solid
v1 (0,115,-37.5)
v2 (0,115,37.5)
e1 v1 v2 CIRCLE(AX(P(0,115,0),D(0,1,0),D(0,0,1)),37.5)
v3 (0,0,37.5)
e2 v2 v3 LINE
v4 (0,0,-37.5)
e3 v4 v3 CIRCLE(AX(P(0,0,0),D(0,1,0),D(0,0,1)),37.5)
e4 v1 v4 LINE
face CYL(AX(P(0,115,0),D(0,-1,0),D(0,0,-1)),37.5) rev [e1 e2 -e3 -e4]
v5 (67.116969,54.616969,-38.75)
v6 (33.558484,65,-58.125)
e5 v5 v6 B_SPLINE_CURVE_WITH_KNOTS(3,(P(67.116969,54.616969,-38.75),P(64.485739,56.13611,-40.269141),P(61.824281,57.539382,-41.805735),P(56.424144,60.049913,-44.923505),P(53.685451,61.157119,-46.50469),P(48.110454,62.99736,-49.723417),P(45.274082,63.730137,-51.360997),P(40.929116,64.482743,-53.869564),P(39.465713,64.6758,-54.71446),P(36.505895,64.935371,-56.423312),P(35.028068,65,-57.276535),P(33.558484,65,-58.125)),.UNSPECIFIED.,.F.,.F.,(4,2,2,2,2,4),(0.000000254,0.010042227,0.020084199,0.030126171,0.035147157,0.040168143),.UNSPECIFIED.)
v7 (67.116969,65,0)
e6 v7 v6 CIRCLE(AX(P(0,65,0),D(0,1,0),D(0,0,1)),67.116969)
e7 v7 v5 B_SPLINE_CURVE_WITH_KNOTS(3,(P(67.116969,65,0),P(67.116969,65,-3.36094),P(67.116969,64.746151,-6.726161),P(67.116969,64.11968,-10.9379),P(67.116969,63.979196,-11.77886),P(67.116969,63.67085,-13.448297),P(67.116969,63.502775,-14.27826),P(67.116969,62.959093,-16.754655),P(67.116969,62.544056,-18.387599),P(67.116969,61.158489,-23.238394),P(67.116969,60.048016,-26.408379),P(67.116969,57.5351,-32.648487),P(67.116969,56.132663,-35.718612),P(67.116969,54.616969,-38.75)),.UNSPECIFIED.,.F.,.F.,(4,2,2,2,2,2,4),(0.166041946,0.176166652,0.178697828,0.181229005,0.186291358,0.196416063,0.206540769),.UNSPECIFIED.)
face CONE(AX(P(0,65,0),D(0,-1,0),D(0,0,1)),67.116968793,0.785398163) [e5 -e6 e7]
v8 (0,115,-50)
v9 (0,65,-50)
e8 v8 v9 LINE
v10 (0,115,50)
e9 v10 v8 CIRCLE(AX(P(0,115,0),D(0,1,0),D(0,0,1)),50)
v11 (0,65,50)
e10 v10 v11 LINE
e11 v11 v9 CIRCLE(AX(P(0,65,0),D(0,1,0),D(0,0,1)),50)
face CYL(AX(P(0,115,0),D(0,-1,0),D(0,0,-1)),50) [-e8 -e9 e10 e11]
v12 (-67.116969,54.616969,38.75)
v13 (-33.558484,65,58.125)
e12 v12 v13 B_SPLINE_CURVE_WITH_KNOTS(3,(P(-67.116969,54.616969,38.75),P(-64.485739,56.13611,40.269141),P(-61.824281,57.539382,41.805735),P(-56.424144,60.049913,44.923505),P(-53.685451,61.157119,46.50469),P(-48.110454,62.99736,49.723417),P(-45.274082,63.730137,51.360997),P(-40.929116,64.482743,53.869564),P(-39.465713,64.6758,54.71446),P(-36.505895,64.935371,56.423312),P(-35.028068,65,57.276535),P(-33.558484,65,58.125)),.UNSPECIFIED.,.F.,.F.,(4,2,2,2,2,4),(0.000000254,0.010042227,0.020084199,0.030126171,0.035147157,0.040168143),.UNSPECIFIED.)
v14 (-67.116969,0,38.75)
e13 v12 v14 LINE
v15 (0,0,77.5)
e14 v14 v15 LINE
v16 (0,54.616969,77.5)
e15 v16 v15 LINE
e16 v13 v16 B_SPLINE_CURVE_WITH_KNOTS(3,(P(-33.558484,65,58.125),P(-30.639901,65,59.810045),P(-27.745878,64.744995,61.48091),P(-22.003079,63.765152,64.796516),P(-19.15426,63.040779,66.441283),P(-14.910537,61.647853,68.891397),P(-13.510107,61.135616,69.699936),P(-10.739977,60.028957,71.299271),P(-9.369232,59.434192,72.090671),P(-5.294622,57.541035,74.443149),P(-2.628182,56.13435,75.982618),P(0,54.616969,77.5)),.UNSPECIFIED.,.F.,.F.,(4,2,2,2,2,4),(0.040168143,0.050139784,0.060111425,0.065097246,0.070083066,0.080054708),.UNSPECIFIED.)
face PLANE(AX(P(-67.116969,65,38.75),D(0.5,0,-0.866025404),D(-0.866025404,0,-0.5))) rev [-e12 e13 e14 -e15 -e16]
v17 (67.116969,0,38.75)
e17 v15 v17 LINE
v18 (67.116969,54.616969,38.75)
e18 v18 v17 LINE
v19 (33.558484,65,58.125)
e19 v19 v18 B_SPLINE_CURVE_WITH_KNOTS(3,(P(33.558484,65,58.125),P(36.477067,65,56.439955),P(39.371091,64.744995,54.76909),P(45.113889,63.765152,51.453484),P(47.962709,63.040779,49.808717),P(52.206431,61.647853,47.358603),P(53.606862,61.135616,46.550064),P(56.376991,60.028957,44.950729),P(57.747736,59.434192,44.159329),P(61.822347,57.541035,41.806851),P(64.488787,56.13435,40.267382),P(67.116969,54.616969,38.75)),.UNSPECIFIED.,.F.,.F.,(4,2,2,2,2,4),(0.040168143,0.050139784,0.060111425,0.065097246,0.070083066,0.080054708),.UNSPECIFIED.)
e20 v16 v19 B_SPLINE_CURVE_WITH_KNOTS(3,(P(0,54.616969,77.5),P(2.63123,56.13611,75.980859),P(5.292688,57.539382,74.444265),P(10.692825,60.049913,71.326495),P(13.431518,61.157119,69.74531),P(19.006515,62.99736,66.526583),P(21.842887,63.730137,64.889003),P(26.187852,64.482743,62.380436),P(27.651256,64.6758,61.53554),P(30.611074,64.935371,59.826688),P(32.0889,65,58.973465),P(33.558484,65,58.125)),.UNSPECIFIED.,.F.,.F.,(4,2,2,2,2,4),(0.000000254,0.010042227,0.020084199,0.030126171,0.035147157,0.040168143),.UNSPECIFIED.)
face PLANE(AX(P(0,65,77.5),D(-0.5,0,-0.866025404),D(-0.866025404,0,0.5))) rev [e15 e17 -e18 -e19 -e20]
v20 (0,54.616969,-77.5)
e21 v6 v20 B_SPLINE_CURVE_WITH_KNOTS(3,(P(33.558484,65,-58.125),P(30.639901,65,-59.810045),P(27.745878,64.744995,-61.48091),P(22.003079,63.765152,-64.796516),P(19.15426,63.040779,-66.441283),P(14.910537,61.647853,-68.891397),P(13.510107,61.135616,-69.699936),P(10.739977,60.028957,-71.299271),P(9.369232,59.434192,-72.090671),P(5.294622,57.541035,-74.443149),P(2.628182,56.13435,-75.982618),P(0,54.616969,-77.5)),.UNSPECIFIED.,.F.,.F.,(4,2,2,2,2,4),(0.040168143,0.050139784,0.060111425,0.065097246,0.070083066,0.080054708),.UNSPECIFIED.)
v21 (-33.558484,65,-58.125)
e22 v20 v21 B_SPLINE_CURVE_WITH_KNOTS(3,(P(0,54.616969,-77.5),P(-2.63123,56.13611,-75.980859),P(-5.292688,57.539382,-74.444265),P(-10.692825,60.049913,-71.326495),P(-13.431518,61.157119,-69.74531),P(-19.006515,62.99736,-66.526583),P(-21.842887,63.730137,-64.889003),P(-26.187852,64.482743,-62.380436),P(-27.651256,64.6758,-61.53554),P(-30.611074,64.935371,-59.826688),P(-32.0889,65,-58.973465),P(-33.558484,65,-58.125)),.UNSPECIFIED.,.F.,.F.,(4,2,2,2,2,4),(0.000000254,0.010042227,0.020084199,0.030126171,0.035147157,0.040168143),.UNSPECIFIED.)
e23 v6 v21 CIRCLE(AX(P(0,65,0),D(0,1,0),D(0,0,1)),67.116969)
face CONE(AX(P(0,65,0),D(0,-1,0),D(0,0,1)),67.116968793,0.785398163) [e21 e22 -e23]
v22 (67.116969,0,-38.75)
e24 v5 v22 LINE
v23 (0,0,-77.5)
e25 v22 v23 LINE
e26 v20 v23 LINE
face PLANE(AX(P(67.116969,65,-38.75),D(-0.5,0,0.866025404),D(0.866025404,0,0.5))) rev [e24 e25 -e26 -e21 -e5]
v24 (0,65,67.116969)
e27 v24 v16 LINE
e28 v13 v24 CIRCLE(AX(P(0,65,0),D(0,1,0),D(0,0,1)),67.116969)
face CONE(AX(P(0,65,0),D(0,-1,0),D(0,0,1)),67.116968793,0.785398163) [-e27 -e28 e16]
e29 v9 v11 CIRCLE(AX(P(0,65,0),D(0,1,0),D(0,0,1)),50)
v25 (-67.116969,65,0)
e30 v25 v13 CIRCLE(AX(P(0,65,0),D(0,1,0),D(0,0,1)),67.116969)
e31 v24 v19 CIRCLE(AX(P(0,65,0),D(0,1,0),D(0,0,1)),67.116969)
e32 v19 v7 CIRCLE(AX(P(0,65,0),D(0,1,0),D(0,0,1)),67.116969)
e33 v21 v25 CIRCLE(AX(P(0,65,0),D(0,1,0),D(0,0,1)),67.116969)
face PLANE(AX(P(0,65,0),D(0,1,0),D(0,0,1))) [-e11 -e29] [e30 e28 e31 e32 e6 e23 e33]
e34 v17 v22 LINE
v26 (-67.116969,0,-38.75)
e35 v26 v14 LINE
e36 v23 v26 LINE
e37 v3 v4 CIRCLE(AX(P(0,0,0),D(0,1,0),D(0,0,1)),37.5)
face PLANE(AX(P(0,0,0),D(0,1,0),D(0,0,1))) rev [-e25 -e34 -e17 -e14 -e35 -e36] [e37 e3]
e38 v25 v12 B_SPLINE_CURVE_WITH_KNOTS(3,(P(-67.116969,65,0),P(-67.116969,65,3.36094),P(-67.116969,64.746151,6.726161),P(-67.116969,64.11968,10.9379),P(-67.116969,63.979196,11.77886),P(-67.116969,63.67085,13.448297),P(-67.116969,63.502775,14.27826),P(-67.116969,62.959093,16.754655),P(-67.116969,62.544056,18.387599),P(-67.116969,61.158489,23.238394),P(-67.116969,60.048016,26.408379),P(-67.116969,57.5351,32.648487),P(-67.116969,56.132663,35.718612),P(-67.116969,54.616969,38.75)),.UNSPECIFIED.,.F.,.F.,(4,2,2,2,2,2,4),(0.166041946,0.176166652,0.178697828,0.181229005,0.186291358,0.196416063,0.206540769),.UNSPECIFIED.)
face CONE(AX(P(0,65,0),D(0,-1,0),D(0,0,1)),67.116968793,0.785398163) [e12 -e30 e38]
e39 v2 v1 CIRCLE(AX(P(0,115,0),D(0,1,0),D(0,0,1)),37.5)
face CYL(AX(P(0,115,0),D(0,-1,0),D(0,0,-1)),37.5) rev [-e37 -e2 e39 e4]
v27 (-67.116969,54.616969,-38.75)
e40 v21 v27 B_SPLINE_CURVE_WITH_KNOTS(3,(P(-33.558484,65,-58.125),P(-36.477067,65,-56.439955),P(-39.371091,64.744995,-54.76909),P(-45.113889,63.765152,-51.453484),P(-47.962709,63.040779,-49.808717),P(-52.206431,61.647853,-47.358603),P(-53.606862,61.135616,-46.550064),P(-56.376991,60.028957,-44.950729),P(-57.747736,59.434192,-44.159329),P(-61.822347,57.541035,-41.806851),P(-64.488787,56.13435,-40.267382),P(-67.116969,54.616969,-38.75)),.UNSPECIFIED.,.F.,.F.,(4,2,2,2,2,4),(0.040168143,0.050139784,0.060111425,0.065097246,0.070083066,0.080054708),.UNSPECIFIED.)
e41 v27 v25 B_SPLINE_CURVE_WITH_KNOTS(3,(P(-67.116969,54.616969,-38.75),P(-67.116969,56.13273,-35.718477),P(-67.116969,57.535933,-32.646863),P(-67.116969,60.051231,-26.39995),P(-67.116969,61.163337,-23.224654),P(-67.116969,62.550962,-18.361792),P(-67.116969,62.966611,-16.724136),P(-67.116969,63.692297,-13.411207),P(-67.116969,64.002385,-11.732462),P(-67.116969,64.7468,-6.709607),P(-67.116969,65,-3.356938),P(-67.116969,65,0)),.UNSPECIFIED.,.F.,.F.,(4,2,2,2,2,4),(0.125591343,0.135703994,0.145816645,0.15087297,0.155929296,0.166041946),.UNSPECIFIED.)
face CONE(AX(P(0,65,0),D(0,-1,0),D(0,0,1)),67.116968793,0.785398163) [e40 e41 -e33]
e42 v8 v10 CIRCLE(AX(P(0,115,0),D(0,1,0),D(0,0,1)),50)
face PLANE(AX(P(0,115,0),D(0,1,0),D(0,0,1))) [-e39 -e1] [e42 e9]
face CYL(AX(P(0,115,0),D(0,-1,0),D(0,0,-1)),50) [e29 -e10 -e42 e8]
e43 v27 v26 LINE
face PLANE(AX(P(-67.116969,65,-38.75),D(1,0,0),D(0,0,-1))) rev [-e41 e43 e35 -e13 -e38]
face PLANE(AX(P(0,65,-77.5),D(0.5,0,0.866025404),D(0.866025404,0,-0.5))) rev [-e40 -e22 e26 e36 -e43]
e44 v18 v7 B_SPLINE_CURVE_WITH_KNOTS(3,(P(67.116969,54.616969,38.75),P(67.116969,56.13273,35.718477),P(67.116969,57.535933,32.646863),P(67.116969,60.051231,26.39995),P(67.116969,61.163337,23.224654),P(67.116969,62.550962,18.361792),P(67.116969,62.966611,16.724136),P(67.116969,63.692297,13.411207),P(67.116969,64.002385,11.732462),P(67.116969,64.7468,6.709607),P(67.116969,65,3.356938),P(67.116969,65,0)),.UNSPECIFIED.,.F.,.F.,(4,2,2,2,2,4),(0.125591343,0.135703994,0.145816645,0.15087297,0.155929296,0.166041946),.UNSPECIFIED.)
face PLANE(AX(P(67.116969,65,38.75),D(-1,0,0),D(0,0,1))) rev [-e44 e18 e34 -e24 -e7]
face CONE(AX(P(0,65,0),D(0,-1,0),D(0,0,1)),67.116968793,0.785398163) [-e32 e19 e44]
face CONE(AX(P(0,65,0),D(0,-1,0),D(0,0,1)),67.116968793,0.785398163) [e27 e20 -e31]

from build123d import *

# Parameters (mm, degrees)
HEX_BODY_DEPTH                  = 65
CORNER_CHAMFER_SKETCH_OUTSIDE_W = 309.254
CORNER_CHAMFER_SKETCH_OUTSIDE_H = 330.02
CORNER_CHAMFER_SKETCH_OUTSIDE_R = 67.116968793
HEX_CORNER_CHAMFER_45DEG_DEPTH  = 65
HEX_CORNER_CHAMFER_45DEG_DRAFT  = -45
LOCKING_COLLAR_SKETCH_R         = 50
LOCKING_COLLAR_SKETCH_R_2       = 37.5
LOCKING_COLLAR_DEPTH            = 50
NUT_START                       = -120
SKETCH3_2_R                     = 37.5
NUT_BORE_DEPTH                  = 120


with BuildPart() as part:
    # Hex Profile Sketch → Hex Body (new body)
    with BuildSketch(Plane(origin=(0, 0, 0), x_dir=(1, 0, 0), z_dir=(0, 1, 0))):
        Polygon((0, -77.5), (67.116968793, -38.75), (67.116968793, 38.75), (0, 77.5), (-67.116968793, 38.75), (-67.116968793, -38.75), align=None)
    extrude(amount=HEX_BODY_DEPTH)


with BuildPart() as hex_corner_chamfer_45deg_tool:
    # Corner Chamfer Sketch outside → Hex Corner Chamfer 45deg (with draft: the straight prism first)
    with BuildSketch(Plane(origin=(0, 65, 0), x_dir=(1, 0, 0), z_dir=(0, 1, 0))):
        Rectangle(CORNER_CHAMFER_SKETCH_OUTSIDE_W, CORNER_CHAMFER_SKETCH_OUTSIDE_H)
        Circle(CORNER_CHAMFER_SKETCH_OUTSIDE_R, mode=Mode.SUBTRACT)
    extrude(amount=-HEX_CORNER_CHAMFER_45DEG_DEPTH)
    # Hex Corner Chamfer 45deg: the draft: its side faces are tilted about the plane it starts from
    hex_corner_chamfer_45deg_sides = [hex_corner_chamfer_45deg_tool.faces().sort_by_distance(p)[0] for p in [
        (0, 32.5, 165.01),
        (154.627, 32.5, 0),
        (0, 32.5, -165.01),
        (-154.627, 32.5, 0),
        (-67.116968793, 32.5, 0),
    ]]
    draft(hex_corner_chamfer_45deg_sides, Plane(origin=(0, 65, 0), x_dir=(1, 0, 0), z_dir=(0, 1, 0)), HEX_CORNER_CHAMFER_45DEG_DRAFT)


with BuildPart() as part_1:
    add(part.part)

    # Hex Corner Chamfer 45deg: cut by hex_corner_chamfer_45deg_tool
    add(hex_corner_chamfer_45deg_tool.part, mode=Mode.SUBTRACT)

    # Locking Collar Sketch → Locking Collar (add)
    with BuildSketch(Plane(origin=(0, 65, 0), x_dir=(1, 0, 0), z_dir=(0, 1, 0))):
        with Locations(Location((0, 0, 0), (0, 0, 270))):
            Circle(LOCKING_COLLAR_SKETCH_R)
        with Locations(Location((0, 0, 0), (0, 0, 270))):
            Circle(LOCKING_COLLAR_SKETCH_R_2, mode=Mode.SUBTRACT)
    extrude(amount=LOCKING_COLLAR_DEPTH)

    # Sketch3_2 → Nut Bore (cut)
    with BuildSketch(Plane(origin=(0, 65, 0), x_dir=(1, 0, 0), z_dir=(0, 1, 0)).offset(NUT_START)):
        with Locations(Location((0, 0, 0), (0, 0, 270))):
            Circle(SKETCH3_2_R)
    extrude(amount=NUT_BORE_DEPTH, mode=Mode.SUBTRACT)


solid = part_1.part
